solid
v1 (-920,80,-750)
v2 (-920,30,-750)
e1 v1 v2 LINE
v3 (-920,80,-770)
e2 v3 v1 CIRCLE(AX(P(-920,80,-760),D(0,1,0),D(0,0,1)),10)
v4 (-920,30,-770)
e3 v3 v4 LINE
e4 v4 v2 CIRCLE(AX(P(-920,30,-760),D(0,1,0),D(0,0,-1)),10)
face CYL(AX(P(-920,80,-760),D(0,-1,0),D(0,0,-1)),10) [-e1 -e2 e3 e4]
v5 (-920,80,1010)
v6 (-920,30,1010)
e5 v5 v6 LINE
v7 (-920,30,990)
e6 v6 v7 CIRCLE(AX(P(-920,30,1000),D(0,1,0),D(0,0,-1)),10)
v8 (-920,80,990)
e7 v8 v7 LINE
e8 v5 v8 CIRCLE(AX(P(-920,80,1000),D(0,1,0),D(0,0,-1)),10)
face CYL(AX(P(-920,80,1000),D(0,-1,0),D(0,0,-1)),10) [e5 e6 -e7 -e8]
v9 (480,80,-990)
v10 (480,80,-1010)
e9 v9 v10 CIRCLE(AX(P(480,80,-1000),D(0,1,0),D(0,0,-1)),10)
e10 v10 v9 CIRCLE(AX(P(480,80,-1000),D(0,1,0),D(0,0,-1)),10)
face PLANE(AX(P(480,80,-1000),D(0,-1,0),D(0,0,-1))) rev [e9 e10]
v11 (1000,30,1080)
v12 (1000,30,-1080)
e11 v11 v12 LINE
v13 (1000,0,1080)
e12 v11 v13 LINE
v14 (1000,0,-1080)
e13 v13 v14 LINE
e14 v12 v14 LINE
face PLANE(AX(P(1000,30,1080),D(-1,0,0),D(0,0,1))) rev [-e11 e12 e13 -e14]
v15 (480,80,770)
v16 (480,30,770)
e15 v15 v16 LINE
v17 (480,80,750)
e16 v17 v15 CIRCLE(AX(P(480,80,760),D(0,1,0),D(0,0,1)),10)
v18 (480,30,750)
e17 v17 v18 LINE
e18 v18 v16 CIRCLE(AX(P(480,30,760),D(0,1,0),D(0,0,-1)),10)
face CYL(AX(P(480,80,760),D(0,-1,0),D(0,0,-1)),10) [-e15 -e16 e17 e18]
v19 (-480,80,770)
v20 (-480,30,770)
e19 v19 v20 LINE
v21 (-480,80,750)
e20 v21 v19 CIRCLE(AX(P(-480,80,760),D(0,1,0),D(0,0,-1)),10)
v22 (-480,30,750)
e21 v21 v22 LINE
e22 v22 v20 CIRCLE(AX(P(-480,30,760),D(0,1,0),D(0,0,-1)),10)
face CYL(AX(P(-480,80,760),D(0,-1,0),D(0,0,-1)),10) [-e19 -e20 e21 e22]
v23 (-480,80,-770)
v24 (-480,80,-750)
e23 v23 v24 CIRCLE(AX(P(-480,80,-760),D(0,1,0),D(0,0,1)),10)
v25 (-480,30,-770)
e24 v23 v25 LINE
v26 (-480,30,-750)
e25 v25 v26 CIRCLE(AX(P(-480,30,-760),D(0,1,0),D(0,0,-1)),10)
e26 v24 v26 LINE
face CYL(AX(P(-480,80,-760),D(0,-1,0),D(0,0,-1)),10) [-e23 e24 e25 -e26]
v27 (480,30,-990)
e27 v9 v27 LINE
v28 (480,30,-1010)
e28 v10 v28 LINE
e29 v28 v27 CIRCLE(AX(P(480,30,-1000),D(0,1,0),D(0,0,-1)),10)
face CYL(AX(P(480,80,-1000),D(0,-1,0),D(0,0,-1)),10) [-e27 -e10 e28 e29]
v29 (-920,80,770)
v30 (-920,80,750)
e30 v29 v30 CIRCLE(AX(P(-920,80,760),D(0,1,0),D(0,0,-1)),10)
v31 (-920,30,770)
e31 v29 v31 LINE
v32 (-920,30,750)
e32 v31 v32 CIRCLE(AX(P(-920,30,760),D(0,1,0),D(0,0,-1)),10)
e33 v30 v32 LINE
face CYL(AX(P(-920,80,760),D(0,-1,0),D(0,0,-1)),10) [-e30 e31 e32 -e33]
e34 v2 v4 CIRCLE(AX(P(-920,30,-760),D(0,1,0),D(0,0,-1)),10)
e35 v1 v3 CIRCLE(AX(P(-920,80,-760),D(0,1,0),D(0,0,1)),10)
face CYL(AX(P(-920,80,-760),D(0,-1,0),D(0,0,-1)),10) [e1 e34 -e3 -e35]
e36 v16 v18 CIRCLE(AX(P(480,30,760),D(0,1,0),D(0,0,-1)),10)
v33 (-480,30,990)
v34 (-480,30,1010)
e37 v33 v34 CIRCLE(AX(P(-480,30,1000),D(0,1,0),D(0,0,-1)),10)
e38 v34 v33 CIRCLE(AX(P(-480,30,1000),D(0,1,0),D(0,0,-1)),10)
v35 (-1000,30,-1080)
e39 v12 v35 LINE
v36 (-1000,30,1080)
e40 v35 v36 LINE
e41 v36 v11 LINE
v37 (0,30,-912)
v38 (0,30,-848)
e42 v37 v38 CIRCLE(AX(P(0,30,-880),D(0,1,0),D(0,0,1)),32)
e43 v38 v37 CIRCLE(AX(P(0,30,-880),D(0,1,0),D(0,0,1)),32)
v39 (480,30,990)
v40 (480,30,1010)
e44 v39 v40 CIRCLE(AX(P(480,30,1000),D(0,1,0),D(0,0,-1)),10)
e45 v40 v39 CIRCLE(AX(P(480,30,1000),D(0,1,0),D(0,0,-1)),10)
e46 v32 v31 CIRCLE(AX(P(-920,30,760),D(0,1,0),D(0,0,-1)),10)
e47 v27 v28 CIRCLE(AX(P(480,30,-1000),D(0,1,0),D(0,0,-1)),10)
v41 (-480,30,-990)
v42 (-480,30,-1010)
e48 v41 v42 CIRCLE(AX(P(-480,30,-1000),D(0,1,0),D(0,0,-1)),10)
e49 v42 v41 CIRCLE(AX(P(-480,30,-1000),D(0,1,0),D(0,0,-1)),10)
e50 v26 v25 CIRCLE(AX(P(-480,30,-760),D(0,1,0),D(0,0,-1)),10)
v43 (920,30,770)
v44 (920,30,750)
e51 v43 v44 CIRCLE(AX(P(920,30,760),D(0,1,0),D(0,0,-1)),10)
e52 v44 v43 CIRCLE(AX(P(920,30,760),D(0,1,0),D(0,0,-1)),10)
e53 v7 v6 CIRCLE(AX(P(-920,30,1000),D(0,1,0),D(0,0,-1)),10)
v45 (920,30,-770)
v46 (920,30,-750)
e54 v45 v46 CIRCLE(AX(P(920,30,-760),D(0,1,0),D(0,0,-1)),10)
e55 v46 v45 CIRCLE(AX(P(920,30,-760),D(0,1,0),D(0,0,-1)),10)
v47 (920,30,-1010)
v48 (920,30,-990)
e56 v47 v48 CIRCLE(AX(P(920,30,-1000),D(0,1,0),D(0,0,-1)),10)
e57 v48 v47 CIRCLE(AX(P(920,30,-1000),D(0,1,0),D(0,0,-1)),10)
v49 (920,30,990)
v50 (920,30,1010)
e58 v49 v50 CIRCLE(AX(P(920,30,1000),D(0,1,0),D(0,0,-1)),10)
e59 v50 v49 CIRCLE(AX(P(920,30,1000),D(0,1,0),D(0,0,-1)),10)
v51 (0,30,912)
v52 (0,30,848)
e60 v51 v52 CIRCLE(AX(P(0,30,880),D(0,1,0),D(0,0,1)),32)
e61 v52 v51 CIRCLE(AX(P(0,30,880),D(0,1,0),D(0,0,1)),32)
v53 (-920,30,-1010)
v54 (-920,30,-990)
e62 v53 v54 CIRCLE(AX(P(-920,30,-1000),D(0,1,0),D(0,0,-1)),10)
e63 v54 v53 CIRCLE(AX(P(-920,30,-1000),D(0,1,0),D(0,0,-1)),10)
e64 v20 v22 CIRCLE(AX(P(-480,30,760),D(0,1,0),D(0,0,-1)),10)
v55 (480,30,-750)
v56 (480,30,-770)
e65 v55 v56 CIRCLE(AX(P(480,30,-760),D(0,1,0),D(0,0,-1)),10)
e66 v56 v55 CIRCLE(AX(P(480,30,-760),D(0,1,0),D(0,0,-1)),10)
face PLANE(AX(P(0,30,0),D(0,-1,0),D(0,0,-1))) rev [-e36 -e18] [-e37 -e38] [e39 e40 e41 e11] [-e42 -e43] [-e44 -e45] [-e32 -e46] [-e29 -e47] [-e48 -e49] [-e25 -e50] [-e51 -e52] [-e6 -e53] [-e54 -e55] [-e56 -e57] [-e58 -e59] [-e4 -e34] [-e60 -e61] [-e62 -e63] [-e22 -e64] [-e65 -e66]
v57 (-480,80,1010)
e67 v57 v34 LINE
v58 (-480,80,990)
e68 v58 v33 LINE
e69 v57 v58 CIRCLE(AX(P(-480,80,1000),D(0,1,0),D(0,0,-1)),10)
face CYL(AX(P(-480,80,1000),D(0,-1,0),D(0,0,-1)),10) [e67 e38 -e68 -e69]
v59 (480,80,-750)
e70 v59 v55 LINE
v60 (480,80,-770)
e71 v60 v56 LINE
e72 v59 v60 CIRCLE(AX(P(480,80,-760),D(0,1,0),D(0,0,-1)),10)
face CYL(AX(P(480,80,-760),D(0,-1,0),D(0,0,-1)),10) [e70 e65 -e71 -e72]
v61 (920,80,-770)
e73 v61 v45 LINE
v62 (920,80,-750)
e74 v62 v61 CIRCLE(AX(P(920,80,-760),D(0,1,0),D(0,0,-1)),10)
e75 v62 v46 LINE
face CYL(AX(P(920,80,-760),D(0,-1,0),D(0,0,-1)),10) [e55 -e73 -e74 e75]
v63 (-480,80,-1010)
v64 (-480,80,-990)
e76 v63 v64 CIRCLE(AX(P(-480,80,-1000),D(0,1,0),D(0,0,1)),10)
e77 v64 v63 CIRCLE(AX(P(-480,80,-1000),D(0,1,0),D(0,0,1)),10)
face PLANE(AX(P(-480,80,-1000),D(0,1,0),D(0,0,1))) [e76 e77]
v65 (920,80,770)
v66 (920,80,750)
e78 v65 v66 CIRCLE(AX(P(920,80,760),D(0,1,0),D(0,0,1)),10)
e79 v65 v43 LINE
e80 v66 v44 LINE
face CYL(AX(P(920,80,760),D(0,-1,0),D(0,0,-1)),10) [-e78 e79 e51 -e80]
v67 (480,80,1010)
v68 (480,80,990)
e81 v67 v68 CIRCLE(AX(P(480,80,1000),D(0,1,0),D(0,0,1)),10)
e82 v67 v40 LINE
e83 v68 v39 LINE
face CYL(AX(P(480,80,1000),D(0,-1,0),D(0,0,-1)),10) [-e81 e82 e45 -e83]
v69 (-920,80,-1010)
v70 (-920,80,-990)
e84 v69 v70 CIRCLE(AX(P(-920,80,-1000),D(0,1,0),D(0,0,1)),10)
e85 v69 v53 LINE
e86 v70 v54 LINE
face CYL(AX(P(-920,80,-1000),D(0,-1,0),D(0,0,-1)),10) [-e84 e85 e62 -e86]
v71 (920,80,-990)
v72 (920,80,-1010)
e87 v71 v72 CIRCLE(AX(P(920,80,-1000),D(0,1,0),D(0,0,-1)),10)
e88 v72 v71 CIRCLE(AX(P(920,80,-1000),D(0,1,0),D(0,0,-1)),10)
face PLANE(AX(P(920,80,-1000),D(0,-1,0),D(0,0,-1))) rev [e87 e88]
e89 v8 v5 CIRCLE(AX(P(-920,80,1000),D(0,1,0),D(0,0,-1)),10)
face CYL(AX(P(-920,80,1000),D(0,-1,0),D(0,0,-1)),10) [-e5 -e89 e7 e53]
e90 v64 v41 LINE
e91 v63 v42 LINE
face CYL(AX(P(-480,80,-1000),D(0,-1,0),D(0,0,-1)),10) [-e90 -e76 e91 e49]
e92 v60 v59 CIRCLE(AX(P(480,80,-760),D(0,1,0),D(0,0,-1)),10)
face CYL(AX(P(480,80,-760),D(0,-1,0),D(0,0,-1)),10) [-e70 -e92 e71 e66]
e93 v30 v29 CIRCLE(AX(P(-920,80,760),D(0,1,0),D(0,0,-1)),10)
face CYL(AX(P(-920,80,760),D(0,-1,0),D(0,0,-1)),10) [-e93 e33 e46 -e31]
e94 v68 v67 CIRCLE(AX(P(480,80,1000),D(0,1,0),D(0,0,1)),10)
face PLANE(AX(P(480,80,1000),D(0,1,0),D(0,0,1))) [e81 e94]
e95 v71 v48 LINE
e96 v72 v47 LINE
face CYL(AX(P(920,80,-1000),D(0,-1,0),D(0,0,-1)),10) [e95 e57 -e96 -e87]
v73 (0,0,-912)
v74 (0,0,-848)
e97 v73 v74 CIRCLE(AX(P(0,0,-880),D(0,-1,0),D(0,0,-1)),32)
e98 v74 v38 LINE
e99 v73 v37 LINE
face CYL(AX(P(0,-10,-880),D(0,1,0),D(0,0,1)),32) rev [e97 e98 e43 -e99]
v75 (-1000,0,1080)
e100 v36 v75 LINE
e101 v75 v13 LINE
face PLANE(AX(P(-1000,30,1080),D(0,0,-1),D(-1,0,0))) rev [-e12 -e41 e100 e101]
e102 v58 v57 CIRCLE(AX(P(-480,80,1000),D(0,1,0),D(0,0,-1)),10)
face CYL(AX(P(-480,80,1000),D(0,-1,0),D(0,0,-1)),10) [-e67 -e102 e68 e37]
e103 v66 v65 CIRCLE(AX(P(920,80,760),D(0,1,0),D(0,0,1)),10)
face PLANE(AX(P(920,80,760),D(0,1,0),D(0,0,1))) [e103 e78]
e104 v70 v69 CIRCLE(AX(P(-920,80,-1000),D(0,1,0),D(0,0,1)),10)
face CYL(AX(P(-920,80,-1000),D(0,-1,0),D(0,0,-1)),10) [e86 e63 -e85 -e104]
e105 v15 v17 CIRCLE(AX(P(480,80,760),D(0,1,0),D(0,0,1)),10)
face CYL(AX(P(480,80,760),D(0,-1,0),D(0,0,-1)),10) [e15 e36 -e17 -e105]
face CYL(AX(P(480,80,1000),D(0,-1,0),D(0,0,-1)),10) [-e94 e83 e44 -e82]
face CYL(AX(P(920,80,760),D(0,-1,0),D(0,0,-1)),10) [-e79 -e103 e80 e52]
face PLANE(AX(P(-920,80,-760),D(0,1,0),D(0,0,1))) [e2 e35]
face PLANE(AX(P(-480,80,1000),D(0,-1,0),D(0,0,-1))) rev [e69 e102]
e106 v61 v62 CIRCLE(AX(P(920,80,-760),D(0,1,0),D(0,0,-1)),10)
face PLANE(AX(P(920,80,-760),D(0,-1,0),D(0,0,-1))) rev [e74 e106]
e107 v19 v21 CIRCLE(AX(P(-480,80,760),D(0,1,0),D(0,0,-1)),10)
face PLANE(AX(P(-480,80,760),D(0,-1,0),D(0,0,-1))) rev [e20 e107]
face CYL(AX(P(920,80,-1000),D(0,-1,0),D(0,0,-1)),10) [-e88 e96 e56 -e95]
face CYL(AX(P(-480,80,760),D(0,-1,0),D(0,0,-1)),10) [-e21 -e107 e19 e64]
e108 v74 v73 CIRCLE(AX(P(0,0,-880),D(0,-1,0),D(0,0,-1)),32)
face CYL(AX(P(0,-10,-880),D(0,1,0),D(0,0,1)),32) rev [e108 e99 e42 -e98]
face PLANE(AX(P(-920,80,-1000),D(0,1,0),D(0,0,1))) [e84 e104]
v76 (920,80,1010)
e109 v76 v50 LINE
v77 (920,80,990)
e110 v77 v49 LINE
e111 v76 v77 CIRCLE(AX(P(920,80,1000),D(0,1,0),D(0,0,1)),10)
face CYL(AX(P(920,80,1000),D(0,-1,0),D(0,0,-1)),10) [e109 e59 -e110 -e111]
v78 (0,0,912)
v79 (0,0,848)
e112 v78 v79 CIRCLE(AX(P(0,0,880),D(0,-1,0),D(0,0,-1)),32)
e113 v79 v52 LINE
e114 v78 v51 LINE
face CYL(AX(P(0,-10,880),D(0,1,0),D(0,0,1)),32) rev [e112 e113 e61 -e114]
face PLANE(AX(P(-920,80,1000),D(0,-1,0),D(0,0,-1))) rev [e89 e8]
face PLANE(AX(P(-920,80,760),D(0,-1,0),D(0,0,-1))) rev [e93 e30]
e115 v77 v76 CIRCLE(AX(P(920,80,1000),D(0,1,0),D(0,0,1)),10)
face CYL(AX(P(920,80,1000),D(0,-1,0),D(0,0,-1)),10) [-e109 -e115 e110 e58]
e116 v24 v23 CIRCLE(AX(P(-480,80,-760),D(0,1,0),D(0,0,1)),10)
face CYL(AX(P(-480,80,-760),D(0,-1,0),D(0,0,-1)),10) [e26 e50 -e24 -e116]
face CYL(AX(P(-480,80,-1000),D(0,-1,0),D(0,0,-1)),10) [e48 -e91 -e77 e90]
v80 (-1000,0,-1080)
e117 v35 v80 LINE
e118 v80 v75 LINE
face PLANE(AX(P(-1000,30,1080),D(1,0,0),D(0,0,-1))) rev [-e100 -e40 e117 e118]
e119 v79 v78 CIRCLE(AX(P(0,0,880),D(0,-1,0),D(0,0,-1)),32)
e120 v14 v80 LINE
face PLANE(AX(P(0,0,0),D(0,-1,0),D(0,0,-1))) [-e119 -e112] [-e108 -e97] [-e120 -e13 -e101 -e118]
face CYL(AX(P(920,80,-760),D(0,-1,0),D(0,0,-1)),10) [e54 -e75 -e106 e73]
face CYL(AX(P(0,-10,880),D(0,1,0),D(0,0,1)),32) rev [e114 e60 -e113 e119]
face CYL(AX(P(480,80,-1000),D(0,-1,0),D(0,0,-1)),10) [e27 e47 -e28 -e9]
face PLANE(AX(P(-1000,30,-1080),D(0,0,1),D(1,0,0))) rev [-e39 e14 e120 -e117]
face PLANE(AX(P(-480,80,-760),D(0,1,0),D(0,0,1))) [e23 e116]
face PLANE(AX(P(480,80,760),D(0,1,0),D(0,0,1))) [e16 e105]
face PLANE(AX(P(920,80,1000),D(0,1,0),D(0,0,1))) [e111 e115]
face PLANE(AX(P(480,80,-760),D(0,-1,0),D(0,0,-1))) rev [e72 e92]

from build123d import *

# Parameters (mm, degrees)
SKETCH1_W           = 2000
SKETCH1_H           = 2160
BOSS_EXTRUDE1_DEPTH = 30
SKETCH2_R           = 10
BOSS_EXTRUDE2_DEPTH = 50
SKETCH3_R           = 32
CUT_EXTRUDE1_DEPTH  = 40


with BuildPart() as part:
    # Sketch1 → Boss-Extrude1 (new body)
    with BuildSketch(Plane(origin=(0, 0, 0), x_dir=(1, 0, 0), z_dir=(0, 1, 0))):
        Rectangle(SKETCH1_W, SKETCH1_H)
    extrude(amount=BOSS_EXTRUDE1_DEPTH)

    # Sketch2 → Boss-Extrude2 (add)
    with BuildSketch(Plane(origin=(0, 30, 0), x_dir=(1, 0, 0), z_dir=(0, 1, 0))):
        with Locations(Location((-920, 1000, 0), (0, 0, 90))):
            Circle(SKETCH2_R)
        with Locations(Location((-920, 760, 0), (0, 0, 90))):
            Circle(SKETCH2_R)
        with Locations(Location((-480, 1000, 0), (0, 0, 90))):
            Circle(SKETCH2_R)
        with Locations(Location((-480, 760, 0), (0, 0, 90))):
            Circle(SKETCH2_R)
        with Locations(Location((480, 760, 0), (0, 0, 90))):
            Circle(SKETCH2_R)
        with Locations(Location((480, 1000, 0), (0, 0, 90))):
            Circle(SKETCH2_R)
        with Locations(Location((920, 760, 0), (0, 0, 90))):
            Circle(SKETCH2_R)
        with Locations(Location((920, 1000, 0), (0, 0, 90))):
            Circle(SKETCH2_R)
        with Locations(Location((920, -1000, 0), (0, 0, 90))):
            Circle(SKETCH2_R)
        with Locations(Location((920, -760, 0), (0, 0, 90))):
            Circle(SKETCH2_R)
        with Locations(Location((480, -1000, 0), (0, 0, 90))):
            Circle(SKETCH2_R)
        with Locations(Location((480, -760, 0), (0, 0, 90))):
            Circle(SKETCH2_R)
        with Locations(Location((-480, -760, 0), (0, 0, 90))):
            Circle(SKETCH2_R)
        with Locations(Location((-480, -1000, 0), (0, 0, 90))):
            Circle(SKETCH2_R)
        with Locations(Location((-920, -760, 0), (0, 0, 90))):
            Circle(SKETCH2_R)
        with Locations(Location((-920, -1000, 0), (0, 0, 90))):
            Circle(SKETCH2_R)
    extrude(amount=BOSS_EXTRUDE2_DEPTH)

    # Sketch3 → Cut-Extrude1 (cut)
    with BuildSketch(Plane(origin=(0, 30, 0), x_dir=(1, 0, 0), z_dir=(0, 1, 0))):
        with Locations(Location((0, 880, 0), (0, 0, 270))):
            Circle(SKETCH3_R)
        with Locations(Location((0, -880, 0), (0, 0, 270))):
            Circle(SKETCH3_R)
    extrude(amount=-CUT_EXTRUDE1_DEPTH, mode=Mode.SUBTRACT)


solid = part.part
